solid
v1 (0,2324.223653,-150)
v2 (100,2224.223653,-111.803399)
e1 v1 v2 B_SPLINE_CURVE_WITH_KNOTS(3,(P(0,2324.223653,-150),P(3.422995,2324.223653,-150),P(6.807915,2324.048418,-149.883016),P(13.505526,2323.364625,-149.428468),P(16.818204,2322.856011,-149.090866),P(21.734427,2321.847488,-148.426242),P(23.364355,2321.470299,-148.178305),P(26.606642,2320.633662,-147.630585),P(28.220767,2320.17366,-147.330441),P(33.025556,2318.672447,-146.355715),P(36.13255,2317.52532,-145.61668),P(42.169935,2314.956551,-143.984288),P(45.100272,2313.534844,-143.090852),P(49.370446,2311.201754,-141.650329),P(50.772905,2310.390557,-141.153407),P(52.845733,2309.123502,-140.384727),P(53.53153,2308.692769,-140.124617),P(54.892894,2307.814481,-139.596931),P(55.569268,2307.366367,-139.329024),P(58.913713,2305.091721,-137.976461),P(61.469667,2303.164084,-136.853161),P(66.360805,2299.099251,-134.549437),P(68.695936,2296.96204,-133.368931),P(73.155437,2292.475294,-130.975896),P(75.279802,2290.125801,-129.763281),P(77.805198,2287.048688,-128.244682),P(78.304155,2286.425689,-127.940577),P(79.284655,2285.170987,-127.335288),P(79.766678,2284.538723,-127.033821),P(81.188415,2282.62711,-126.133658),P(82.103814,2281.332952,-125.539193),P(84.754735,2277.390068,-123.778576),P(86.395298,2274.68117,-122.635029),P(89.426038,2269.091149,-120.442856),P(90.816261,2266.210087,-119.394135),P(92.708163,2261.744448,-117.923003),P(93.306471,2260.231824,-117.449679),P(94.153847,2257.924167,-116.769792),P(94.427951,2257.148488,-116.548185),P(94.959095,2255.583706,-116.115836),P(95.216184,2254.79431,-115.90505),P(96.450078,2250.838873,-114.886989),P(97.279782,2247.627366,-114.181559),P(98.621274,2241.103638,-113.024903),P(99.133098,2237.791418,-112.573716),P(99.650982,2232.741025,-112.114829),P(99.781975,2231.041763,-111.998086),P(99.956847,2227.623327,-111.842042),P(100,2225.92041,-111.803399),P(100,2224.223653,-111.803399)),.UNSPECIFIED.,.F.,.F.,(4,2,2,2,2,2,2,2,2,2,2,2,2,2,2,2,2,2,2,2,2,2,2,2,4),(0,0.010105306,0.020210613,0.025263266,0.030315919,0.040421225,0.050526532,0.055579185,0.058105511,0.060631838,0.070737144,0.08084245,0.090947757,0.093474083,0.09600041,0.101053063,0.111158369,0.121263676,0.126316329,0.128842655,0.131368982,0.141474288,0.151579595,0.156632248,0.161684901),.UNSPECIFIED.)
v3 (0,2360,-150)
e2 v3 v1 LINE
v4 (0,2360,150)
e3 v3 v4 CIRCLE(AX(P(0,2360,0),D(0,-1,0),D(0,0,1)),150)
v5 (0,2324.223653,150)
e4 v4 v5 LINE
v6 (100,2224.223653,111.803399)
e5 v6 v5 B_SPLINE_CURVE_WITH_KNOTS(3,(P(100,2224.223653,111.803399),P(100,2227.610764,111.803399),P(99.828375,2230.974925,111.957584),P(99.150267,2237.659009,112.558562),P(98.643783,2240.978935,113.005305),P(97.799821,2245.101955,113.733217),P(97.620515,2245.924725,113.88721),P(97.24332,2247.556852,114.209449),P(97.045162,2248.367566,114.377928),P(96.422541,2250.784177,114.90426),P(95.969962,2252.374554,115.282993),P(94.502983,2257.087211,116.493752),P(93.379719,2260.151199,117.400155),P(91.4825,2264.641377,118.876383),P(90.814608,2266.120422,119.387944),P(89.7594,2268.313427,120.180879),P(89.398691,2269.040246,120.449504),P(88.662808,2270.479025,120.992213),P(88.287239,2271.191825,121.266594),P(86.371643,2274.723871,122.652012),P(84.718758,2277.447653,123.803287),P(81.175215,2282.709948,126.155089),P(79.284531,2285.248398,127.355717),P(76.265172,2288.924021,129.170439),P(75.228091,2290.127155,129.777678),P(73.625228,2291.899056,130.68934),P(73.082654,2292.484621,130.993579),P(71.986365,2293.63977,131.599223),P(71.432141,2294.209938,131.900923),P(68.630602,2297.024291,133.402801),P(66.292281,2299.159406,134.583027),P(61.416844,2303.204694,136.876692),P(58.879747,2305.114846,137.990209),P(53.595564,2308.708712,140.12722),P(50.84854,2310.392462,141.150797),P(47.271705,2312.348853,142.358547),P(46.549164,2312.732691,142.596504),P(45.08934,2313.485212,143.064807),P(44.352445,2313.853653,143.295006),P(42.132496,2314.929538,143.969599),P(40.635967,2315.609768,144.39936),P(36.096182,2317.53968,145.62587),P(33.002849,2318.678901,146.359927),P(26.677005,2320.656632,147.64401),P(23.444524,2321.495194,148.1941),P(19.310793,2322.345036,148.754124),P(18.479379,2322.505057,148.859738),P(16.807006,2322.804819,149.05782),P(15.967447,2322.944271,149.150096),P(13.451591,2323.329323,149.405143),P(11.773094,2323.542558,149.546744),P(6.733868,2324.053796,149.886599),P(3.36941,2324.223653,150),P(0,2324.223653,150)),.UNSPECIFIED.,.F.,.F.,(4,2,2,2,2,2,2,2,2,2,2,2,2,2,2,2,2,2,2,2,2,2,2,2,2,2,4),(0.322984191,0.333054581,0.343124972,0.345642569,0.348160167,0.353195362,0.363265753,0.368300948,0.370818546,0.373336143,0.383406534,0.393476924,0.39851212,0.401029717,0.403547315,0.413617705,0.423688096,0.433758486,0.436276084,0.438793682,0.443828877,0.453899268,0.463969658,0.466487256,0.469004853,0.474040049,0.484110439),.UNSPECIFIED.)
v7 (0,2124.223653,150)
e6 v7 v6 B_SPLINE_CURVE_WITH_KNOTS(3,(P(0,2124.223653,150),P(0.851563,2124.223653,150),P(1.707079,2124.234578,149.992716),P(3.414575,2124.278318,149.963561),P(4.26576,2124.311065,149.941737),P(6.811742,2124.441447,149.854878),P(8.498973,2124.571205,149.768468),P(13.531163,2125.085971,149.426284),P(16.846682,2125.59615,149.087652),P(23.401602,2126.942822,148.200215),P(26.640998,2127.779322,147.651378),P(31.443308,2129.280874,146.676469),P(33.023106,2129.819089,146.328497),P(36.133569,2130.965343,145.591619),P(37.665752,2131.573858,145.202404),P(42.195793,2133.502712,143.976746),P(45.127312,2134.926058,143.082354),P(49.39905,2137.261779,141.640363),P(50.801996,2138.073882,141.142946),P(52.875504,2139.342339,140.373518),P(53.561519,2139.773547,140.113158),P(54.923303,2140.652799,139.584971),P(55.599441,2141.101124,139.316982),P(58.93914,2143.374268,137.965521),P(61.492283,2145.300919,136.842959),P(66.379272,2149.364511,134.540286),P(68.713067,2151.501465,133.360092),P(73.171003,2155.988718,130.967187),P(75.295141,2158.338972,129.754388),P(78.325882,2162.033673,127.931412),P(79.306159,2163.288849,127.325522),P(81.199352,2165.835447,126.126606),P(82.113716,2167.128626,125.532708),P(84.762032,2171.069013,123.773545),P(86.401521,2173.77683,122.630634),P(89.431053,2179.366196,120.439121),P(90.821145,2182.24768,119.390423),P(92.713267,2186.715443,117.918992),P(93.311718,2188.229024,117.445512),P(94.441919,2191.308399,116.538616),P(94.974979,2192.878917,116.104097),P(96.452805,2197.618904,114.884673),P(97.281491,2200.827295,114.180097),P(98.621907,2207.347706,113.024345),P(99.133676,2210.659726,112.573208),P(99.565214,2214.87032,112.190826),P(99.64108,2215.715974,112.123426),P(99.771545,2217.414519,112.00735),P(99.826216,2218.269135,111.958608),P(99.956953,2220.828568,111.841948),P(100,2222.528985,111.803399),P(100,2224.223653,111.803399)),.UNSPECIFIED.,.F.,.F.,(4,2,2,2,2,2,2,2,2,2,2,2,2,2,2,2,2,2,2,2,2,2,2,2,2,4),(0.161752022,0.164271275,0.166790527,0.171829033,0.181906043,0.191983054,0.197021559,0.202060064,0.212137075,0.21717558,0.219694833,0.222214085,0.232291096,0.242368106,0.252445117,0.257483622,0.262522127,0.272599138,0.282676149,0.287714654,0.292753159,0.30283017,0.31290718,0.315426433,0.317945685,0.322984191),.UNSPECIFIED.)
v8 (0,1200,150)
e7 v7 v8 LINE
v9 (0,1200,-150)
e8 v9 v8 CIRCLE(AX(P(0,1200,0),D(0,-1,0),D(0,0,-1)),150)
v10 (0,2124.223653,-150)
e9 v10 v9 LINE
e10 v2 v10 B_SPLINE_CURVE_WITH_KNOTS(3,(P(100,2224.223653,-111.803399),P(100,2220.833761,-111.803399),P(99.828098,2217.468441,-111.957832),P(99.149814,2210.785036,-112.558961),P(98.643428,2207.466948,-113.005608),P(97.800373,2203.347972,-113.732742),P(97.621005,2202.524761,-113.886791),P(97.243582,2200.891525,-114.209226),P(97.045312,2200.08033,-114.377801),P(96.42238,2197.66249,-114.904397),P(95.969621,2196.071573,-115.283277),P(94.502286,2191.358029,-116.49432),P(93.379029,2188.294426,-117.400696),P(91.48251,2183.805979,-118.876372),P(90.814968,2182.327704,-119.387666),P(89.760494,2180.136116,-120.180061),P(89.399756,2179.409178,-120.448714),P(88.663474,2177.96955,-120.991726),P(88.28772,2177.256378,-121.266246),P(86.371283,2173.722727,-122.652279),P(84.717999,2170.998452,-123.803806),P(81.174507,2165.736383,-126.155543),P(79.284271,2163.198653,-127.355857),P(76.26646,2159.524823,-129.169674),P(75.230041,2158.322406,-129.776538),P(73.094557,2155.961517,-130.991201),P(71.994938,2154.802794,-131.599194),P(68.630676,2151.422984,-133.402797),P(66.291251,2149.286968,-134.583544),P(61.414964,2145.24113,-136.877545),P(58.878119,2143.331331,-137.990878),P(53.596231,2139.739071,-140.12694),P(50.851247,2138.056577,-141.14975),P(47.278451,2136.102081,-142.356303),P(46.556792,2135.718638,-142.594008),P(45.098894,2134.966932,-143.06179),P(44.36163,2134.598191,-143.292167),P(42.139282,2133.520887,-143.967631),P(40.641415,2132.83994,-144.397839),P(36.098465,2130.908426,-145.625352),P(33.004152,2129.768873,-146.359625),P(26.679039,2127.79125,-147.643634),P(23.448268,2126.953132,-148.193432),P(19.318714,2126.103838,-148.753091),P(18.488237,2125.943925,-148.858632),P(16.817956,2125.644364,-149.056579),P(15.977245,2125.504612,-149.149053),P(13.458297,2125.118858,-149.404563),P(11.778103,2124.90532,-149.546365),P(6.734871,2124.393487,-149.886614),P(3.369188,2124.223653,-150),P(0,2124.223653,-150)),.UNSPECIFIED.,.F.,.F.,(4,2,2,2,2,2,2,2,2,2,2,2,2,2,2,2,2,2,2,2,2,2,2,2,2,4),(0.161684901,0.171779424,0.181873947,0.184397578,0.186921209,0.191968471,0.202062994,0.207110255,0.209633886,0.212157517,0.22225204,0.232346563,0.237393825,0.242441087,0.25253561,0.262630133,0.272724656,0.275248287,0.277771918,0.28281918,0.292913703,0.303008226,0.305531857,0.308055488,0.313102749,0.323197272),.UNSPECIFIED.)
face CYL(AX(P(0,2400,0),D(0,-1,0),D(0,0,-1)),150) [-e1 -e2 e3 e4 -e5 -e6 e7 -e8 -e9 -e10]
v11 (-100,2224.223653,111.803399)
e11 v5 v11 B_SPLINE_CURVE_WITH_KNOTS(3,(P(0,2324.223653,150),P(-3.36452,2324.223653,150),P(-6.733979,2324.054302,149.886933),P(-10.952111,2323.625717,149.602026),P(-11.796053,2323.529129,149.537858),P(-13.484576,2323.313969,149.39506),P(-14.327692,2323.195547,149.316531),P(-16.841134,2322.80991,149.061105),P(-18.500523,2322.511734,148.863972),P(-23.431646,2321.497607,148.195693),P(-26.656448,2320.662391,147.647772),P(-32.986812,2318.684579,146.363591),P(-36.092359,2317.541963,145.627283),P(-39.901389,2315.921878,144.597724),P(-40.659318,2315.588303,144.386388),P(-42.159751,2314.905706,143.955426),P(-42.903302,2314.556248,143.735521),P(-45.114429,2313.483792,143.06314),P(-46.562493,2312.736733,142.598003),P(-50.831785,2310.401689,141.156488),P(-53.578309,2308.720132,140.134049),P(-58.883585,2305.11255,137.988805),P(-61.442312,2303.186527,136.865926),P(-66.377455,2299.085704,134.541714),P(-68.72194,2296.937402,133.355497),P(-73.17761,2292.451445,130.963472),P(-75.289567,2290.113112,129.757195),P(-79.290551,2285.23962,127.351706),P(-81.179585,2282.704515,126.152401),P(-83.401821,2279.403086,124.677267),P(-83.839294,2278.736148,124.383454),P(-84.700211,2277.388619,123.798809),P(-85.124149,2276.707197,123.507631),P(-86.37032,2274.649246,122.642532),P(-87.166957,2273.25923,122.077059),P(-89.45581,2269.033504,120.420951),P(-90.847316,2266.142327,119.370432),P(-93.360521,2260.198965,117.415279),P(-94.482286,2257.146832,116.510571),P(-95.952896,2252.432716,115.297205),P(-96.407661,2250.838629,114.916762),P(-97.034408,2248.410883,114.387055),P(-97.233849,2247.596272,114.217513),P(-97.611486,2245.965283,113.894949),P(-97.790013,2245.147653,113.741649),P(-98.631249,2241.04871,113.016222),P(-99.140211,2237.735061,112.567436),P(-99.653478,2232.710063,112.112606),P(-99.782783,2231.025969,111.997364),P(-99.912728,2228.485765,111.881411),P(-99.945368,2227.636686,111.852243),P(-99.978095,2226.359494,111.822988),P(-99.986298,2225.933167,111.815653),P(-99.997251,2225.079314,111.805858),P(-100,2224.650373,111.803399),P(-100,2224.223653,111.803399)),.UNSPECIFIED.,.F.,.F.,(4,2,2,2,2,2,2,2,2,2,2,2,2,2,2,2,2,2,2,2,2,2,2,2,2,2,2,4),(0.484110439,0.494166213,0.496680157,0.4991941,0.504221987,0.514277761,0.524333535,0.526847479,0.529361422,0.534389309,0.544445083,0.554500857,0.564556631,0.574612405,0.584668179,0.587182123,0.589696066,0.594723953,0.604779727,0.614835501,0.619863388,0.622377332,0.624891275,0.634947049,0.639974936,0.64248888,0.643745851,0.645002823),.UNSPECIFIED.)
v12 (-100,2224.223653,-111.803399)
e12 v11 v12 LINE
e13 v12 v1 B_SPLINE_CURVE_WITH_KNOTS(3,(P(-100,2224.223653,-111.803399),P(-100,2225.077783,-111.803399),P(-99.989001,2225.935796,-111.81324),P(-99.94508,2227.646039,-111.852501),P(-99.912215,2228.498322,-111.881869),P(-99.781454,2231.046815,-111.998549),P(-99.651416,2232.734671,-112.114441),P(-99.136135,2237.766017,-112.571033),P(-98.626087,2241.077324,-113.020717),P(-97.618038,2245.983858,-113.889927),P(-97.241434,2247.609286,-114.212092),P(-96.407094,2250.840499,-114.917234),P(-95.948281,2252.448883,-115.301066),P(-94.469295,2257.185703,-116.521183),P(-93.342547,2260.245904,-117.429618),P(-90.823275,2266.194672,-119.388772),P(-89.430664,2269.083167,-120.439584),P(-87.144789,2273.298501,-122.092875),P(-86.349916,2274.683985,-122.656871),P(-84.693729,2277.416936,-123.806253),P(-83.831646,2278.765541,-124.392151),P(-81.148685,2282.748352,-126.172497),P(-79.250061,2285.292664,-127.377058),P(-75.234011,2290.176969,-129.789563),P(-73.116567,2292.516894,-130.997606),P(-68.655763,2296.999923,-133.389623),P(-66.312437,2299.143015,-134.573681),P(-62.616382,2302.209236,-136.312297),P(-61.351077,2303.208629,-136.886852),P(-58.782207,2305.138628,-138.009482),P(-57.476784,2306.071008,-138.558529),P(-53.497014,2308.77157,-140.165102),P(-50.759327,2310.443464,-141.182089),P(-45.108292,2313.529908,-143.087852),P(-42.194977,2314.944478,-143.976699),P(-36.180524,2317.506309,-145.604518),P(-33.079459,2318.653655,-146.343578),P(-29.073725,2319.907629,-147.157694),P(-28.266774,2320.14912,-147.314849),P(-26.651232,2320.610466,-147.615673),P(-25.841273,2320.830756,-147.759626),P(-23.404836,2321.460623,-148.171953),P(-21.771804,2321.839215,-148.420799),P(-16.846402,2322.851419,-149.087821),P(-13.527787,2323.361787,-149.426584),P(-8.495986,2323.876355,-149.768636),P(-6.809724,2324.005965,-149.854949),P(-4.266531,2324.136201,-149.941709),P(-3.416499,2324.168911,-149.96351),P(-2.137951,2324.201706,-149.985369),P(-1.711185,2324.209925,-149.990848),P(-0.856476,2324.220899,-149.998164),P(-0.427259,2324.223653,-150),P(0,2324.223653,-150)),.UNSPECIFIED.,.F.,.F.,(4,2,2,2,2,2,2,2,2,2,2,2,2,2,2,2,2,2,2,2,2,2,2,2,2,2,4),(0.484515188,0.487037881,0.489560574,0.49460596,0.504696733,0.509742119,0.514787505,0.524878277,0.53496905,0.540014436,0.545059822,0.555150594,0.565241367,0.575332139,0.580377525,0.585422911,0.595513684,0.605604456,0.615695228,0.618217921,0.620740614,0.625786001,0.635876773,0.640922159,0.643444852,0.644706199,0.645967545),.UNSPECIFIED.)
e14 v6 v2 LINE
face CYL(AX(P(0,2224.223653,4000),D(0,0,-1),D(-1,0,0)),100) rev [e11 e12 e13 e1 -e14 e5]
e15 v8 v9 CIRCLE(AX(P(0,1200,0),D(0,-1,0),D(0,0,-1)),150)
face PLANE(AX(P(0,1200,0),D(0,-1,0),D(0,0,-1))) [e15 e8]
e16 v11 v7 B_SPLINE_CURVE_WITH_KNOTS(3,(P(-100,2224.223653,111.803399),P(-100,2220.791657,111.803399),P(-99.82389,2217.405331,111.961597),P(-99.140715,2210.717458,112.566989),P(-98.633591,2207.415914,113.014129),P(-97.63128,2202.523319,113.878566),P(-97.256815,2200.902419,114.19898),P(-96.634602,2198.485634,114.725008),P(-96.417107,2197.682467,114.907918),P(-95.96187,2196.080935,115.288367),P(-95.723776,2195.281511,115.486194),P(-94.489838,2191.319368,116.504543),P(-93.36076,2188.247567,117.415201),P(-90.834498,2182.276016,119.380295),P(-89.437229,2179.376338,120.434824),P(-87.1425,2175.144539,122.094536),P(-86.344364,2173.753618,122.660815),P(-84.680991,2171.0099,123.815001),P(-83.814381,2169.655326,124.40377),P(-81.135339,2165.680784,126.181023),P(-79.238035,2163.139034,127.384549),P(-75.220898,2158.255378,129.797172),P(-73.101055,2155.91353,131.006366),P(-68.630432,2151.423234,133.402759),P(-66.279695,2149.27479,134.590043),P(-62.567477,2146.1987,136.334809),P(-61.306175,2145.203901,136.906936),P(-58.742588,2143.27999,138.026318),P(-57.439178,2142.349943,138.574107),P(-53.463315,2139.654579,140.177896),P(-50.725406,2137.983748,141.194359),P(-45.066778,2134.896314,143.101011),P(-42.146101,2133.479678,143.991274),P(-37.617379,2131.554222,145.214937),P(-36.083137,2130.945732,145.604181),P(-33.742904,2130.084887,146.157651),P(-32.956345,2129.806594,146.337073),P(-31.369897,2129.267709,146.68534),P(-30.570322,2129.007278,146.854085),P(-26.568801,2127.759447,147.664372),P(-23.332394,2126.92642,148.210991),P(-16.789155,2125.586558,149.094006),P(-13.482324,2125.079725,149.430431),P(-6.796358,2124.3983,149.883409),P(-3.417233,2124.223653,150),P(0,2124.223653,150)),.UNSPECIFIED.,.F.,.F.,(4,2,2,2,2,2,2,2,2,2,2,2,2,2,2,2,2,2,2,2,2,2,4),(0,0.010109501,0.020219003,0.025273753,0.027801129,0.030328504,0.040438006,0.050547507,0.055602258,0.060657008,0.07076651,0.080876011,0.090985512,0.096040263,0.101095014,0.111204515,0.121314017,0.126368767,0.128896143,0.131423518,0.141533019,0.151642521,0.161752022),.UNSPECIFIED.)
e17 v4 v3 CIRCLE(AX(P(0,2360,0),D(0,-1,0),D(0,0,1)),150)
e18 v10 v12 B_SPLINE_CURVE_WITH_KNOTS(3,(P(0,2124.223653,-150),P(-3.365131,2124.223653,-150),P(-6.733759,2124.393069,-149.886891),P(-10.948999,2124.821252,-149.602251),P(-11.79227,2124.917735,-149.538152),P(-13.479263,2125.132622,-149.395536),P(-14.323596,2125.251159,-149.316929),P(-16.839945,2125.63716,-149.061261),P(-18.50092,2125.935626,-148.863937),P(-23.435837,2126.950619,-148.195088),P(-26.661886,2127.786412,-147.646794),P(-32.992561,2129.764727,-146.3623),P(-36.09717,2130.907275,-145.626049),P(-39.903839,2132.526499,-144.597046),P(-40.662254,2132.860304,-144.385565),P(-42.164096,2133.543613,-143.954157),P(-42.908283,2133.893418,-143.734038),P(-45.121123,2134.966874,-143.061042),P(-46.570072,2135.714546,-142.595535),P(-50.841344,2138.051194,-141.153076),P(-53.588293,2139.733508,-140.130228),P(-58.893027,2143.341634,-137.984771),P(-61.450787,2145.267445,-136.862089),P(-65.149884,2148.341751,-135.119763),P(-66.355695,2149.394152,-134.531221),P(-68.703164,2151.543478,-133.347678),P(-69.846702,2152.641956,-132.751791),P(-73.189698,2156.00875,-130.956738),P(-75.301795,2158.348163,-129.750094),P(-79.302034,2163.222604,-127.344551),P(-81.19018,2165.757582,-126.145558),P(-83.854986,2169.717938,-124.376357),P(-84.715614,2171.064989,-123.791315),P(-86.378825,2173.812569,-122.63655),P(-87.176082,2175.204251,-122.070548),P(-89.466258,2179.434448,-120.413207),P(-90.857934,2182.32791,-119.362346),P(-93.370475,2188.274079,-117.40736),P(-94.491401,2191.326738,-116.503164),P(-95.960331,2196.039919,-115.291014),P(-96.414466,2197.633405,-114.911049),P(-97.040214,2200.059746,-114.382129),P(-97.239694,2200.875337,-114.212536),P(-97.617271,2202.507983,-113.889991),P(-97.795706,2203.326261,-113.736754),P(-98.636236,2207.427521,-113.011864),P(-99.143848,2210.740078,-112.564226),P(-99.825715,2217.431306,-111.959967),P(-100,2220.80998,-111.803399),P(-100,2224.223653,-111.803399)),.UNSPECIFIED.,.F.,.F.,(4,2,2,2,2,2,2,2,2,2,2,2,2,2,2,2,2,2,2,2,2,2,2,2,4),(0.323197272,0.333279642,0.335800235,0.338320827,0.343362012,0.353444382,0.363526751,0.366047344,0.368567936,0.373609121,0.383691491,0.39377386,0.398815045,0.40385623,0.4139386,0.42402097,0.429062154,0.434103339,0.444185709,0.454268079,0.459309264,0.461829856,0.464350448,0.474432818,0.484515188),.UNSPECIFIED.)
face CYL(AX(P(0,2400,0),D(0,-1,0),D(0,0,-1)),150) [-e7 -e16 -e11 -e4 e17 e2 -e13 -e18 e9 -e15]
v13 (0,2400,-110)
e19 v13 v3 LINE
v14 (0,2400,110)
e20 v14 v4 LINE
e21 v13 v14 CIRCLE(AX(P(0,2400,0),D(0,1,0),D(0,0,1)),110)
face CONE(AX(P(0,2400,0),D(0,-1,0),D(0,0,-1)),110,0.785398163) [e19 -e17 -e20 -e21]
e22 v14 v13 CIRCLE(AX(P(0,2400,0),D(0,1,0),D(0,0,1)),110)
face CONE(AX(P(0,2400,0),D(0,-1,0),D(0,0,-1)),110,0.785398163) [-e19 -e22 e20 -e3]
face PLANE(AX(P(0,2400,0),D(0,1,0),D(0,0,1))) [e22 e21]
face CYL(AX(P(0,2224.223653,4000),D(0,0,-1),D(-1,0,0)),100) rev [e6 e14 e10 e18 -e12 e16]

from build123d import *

# Parameters (mm, degrees)
SKETCH1_R               = 150
BOSS_EXTRUDE1_DEPTH     = 2400
CUT_EXTRUDE1_DEPTH      = 4000
CUT_EXTRUDE1_DEPTH_BACK = 4000
SKETCH2_R               = 100
SKETCH3_R               = 364.072238149
CUT_EXTRUDE2_DEPTH      = 1200
CHAMFER1_SIZE           = 40


with BuildPart() as part:
    # Sketch1 → Boss-Extrude1 (new body)
    with BuildSketch(Plane(origin=(0, 0, 0), x_dir=(1, 0, 0), z_dir=(0, 1, 0))):
        with Locations(Location((0, 0, 0), (0, 0, 270))):
            Circle(SKETCH1_R)
    extrude(amount=BOSS_EXTRUDE1_DEPTH)

    # Sketch2 → Cut-Extrude1 (cut, two sides: drawn at the far end of the back side and taken through both)
    with BuildSketch(Plane.XY.offset(-CUT_EXTRUDE1_DEPTH_BACK)):
        with Locations(Location((0, 2224.223653396, 0), (0, 0, 89.999999999))):
            Circle(SKETCH2_R)
    extrude(amount=CUT_EXTRUDE1_DEPTH + CUT_EXTRUDE1_DEPTH_BACK, mode=Mode.SUBTRACT)

    # Sketch3 → Cut-Extrude2 (cut)
    with BuildSketch(Plane.XZ):
        Circle(SKETCH3_R)
    extrude(amount=-CUT_EXTRUDE2_DEPTH, mode=Mode.SUBTRACT)

    # Chamfer1
    chamfer1_edges = [part.edges().sort_by_distance(p)[0] for p in [
        (0, 2400, -150),
    ]]
    chamfer(chamfer1_edges, length=CHAMFER1_SIZE)


solid = part.part
